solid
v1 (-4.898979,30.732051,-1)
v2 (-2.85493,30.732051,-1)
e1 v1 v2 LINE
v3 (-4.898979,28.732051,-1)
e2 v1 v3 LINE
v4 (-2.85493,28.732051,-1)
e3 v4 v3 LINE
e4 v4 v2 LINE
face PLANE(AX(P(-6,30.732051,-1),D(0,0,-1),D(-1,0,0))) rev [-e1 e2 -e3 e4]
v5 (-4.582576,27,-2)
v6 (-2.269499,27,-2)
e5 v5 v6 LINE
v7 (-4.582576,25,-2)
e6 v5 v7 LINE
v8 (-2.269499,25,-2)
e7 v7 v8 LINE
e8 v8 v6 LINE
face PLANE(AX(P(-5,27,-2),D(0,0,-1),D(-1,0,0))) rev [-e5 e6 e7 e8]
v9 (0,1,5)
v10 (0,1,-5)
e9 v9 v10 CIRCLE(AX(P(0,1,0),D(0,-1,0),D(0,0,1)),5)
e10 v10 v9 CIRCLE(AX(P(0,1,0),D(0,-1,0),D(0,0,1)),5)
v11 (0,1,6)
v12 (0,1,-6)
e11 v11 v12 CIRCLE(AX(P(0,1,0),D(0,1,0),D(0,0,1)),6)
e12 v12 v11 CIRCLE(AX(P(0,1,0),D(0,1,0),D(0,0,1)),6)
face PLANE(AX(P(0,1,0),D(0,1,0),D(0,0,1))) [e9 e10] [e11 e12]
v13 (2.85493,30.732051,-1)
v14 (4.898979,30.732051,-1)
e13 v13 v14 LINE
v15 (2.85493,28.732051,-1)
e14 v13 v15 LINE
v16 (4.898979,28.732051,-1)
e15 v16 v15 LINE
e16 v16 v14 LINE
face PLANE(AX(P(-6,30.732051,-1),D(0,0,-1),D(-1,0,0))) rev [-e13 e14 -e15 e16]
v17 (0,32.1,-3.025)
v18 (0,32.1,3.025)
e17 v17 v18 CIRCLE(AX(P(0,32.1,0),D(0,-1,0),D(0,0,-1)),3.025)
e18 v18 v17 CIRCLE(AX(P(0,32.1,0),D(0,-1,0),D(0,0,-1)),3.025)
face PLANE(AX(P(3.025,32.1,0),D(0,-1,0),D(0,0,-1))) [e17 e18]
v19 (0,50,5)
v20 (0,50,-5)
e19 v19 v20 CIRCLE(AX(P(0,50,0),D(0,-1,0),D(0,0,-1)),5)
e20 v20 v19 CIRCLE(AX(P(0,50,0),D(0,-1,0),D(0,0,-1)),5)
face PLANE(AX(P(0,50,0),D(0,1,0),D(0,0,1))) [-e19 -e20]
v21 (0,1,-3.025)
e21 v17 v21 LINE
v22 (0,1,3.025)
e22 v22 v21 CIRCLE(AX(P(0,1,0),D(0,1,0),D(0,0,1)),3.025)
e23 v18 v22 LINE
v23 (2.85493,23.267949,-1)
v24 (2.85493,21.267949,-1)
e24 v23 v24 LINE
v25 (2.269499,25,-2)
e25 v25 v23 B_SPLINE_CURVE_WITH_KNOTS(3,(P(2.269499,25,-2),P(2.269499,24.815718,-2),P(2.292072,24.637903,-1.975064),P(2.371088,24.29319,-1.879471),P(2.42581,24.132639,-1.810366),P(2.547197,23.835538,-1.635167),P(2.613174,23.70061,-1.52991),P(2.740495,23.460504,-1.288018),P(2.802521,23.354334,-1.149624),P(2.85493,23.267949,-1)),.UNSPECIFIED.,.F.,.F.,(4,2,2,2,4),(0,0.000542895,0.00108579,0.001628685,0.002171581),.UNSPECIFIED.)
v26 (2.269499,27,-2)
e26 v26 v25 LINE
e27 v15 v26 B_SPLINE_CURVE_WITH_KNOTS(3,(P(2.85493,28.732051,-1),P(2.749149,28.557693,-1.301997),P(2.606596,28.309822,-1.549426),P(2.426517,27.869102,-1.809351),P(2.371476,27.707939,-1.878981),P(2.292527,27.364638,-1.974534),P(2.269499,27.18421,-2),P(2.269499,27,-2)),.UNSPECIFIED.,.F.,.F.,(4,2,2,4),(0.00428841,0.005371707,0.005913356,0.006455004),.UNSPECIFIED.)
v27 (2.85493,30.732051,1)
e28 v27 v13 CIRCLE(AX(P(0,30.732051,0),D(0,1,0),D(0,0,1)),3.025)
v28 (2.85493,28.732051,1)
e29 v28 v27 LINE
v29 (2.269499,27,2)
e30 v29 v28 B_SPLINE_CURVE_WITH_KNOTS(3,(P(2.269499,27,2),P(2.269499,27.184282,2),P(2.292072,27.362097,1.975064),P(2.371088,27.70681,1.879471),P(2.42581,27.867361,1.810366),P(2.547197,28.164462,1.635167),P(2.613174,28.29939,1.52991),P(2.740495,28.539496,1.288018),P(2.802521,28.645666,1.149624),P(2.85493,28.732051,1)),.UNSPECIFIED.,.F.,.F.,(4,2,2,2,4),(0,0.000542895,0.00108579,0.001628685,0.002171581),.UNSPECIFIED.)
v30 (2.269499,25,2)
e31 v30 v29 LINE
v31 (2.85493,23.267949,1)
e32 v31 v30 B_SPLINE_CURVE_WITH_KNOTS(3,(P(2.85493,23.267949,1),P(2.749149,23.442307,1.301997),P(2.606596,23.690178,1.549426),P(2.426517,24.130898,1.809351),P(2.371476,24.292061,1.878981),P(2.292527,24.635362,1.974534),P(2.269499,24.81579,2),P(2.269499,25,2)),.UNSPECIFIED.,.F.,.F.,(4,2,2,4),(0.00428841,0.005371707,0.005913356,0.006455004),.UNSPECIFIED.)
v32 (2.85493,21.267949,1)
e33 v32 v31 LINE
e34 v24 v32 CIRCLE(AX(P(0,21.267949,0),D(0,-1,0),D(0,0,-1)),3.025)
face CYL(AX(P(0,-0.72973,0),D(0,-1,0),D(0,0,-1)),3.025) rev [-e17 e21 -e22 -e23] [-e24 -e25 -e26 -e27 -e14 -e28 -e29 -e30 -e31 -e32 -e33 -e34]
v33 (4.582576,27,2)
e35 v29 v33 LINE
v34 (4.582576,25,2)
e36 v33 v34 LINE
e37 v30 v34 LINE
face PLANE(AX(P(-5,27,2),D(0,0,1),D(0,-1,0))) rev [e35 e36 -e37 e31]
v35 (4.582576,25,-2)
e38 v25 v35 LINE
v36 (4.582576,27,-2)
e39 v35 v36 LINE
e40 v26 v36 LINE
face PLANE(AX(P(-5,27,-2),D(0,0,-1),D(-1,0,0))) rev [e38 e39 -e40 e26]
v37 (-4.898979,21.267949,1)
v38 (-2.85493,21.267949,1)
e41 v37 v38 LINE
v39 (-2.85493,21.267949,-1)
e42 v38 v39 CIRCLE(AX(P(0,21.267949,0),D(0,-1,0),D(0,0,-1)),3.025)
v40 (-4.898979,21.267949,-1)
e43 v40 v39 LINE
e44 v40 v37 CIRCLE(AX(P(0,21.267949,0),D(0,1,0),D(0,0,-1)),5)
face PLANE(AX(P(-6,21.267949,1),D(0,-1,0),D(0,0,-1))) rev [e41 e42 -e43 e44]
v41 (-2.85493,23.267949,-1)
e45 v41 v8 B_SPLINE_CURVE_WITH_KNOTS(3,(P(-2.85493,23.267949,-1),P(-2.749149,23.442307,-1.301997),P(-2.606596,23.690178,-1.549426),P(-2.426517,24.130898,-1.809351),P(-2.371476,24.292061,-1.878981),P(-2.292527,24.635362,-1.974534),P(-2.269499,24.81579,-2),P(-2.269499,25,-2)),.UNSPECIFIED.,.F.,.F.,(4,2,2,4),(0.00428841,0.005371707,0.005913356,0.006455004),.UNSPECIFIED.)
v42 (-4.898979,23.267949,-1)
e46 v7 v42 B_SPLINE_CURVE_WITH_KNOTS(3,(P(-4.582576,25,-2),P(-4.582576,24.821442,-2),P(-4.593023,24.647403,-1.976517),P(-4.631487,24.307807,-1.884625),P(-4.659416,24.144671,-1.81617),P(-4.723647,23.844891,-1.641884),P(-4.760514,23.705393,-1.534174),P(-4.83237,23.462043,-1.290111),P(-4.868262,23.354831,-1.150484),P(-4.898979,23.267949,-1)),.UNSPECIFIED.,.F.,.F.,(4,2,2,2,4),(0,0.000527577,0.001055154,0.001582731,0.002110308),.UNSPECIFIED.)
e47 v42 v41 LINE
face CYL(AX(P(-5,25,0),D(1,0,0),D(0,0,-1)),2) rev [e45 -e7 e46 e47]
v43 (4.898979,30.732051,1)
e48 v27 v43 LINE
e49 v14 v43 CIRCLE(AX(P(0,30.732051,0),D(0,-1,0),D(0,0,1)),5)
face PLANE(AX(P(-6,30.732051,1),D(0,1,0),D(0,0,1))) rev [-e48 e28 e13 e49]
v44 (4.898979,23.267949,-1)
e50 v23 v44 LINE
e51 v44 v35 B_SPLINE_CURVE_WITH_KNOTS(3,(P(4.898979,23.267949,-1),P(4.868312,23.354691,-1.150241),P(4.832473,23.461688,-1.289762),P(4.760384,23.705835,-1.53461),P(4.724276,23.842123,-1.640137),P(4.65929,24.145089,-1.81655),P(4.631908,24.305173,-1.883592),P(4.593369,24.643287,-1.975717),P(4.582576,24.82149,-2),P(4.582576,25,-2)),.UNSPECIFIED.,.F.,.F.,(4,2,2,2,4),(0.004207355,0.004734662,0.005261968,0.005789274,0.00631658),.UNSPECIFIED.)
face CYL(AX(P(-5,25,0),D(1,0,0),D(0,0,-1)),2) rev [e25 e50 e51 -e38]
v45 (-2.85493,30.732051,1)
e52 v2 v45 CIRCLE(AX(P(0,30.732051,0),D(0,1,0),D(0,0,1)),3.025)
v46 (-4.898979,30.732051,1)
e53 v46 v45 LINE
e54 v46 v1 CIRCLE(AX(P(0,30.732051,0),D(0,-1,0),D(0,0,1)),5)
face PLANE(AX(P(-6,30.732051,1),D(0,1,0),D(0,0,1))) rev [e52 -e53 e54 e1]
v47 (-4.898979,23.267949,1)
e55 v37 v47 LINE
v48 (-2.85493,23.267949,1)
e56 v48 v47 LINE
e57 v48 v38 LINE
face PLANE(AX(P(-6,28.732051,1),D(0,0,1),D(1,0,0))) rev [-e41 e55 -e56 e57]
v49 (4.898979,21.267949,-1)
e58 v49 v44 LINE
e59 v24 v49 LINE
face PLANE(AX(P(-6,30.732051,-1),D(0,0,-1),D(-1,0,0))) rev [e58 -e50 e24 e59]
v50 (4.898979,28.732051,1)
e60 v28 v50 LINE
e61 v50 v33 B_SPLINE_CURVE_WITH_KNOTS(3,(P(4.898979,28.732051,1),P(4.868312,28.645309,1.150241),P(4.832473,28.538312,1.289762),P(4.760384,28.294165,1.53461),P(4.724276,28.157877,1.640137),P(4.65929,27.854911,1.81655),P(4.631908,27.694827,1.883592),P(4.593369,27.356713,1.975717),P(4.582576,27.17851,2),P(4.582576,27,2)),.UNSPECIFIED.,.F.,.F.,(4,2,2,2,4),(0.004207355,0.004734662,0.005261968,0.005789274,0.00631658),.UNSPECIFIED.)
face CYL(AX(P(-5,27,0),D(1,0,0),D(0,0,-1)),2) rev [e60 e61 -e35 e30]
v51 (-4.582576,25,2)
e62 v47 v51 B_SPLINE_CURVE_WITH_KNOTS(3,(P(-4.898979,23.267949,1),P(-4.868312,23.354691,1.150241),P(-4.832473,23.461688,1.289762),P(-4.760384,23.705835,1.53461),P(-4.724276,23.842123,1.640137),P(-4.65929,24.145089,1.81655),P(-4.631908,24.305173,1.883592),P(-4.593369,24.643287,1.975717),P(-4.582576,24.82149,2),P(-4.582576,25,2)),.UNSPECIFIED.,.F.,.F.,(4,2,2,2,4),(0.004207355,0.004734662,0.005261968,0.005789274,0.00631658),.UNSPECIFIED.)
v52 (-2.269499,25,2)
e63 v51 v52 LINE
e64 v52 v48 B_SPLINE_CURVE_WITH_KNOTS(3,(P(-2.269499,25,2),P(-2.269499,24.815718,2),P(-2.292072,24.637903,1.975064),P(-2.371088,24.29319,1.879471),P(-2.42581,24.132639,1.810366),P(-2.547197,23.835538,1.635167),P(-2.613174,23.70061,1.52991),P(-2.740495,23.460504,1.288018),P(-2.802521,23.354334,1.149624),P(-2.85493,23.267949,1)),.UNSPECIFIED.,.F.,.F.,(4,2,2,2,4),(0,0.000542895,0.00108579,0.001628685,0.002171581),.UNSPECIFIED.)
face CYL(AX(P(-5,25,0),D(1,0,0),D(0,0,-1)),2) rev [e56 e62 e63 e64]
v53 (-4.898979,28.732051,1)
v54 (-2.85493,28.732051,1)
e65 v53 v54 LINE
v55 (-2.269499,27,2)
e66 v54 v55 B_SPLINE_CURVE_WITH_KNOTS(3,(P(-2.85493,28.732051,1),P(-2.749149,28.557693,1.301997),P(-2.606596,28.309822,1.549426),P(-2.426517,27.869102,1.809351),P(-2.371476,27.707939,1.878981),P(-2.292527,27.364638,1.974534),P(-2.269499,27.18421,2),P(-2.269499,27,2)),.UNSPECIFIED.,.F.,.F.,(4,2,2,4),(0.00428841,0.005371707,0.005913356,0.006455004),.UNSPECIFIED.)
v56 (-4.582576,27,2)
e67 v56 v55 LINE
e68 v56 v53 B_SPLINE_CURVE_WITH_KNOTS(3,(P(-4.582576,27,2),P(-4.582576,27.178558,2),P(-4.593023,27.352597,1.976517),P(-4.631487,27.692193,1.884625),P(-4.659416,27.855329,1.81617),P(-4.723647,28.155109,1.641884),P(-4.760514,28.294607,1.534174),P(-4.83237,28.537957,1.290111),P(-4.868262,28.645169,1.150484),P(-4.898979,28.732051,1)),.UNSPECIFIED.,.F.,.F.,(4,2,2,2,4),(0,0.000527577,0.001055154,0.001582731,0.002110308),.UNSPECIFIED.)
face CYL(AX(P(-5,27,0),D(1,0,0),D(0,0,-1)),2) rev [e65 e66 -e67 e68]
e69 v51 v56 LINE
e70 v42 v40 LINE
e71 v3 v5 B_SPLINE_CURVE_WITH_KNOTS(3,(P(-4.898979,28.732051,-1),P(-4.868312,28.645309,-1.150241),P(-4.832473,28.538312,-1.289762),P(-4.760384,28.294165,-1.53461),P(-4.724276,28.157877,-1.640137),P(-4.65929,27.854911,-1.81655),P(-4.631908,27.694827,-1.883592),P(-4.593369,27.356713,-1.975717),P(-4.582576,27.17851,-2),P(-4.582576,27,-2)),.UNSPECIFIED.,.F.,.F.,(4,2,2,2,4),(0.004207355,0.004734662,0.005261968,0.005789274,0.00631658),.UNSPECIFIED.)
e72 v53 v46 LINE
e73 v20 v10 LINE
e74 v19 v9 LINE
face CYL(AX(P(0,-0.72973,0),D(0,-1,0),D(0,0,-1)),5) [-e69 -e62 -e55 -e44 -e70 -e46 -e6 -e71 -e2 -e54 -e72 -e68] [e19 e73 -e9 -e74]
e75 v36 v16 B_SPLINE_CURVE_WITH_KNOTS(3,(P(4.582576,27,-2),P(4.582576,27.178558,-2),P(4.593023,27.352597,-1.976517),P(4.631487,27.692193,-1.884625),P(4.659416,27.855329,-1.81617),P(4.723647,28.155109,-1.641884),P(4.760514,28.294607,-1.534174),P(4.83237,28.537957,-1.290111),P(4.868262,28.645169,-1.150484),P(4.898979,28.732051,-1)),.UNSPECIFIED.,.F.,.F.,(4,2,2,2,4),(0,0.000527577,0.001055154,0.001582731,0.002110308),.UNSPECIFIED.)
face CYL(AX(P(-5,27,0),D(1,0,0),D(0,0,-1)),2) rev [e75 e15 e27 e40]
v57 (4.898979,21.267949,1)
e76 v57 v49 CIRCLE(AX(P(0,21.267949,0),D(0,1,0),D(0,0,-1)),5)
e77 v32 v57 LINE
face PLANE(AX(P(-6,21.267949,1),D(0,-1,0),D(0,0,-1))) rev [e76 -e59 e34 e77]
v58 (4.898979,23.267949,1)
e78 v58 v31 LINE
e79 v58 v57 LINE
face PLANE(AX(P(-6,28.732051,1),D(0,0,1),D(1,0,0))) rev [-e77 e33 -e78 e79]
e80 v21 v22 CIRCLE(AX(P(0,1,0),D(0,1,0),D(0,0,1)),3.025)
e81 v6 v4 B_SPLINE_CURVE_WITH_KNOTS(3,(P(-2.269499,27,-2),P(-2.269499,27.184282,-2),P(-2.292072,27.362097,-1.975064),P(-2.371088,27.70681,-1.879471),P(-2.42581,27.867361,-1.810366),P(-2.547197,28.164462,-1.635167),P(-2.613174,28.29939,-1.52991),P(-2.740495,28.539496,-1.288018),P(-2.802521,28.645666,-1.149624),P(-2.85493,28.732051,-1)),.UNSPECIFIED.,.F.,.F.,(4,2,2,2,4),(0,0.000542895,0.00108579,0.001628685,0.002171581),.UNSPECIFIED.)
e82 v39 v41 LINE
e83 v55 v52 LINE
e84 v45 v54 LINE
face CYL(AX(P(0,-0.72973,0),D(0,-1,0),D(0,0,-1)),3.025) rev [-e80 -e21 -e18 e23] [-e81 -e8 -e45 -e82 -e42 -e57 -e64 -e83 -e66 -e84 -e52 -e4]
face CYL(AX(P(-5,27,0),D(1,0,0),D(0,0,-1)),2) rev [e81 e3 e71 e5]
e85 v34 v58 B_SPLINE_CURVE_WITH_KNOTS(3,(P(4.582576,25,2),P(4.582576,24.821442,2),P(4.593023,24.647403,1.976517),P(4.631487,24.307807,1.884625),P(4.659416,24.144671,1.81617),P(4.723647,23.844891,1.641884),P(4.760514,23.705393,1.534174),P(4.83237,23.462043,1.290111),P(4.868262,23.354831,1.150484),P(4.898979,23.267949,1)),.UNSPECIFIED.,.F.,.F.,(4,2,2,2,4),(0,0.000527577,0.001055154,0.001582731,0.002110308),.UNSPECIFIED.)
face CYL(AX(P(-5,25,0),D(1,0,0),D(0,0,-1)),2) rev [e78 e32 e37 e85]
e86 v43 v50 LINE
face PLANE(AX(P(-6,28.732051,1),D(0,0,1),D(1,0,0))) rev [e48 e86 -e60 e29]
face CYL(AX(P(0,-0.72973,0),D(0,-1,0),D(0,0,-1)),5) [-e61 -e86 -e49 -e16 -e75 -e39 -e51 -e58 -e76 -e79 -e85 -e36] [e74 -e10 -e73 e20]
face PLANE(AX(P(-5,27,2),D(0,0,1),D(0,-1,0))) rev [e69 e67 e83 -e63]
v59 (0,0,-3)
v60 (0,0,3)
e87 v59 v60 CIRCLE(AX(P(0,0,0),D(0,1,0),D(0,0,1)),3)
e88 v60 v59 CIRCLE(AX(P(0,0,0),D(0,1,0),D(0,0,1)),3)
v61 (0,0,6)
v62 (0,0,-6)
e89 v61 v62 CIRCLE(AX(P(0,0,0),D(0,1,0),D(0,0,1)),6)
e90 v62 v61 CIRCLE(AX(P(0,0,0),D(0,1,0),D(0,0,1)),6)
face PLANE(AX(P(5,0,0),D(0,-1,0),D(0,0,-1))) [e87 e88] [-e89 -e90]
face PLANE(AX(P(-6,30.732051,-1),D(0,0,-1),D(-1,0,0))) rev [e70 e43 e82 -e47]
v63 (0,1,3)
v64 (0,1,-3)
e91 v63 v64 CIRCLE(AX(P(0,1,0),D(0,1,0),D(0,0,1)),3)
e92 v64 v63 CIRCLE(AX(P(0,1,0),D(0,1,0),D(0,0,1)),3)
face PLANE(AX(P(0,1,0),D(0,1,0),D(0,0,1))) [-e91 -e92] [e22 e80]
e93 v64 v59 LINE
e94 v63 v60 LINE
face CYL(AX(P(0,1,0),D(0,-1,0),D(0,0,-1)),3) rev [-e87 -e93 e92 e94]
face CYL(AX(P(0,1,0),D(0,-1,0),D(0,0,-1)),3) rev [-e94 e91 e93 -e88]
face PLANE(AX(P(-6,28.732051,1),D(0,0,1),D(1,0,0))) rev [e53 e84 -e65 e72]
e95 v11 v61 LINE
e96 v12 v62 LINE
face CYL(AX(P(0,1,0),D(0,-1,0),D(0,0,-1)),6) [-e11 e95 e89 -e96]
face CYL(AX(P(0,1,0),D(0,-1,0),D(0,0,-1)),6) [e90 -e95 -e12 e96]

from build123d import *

# Parameters (mm, degrees)
CUT_EXTRUDE1_DEPTH  = 52.23475383
SKETCH9_R           = 6
SKETCH9_R_2         = 3
BOSS_EXTRUDE3_DEPTH = 1
CUT_EXTRUDE2_DEPTH  = 52.546095972


with BuildPart() as part:
    # Sketch3 → Revolve1 (revolve)
    with BuildSketch(Plane.XY, mode=Mode.PRIVATE) as revolve1_sk:
        Polygon((3.025, 0), (3.025, 32.1), (0, 32.1), (0, 50), (5, 50), (5, 0), align=None)
    revolve(revolve1_sk.sketch.rotate(Axis((0, -0.72972973, 0), (0, 1, 0)), 90), axis=Axis((0, -0.72972973, 0), (0, 1, 0)))

    # Sketch6 → Cut-Extrude1 (cut, through all)
    with BuildSketch(Plane(origin=(5, 0, 0), x_dir=(0, 0, -1), z_dir=(1, 0, 0))):
        with BuildLine():
            Line((2, 27), (2, 25))
            ThreePointArc((2, 25), (0, 23), (-2, 25))
            Line((-2, 25), (-2, 27))
            ThreePointArc((-2, 27), (0, 29), (2, 27))
        make_face()
    extrude(amount=-CUT_EXTRUDE1_DEPTH, mode=Mode.SUBTRACT)

    # Sketch9 → Boss-Extrude3 (add)
    with BuildSketch(Plane(origin=(0, 0, 0), x_dir=(1, 0, 0), z_dir=(0, 1, 0))):
        with Locations(Location((0, 0, 0), (0, 0, 270))):
            Circle(SKETCH9_R)
        with Locations(Location((0, 0, 0), (0, 0, 270))):
            Circle(SKETCH9_R_2, mode=Mode.SUBTRACT)
    extrude(amount=BOSS_EXTRUDE3_DEPTH)

    # Sketch11 → Cut-Extrude2 (cut, through all)
    with BuildSketch(Plane(origin=(5, 0, 0), x_dir=(0, 0, -1), z_dir=(1, 0, 0))):
        Polygon((-1, 23.267949192), (-1, 21.267949192), (1, 21.267949192), (1, 23.267949192), (1, 28.732050808), (1, 30.732050808), (-1, 30.732050808), (-1, 28.732050808), align=None)
    extrude(amount=-CUT_EXTRUDE2_DEPTH, mode=Mode.SUBTRACT)


solid = part.part
